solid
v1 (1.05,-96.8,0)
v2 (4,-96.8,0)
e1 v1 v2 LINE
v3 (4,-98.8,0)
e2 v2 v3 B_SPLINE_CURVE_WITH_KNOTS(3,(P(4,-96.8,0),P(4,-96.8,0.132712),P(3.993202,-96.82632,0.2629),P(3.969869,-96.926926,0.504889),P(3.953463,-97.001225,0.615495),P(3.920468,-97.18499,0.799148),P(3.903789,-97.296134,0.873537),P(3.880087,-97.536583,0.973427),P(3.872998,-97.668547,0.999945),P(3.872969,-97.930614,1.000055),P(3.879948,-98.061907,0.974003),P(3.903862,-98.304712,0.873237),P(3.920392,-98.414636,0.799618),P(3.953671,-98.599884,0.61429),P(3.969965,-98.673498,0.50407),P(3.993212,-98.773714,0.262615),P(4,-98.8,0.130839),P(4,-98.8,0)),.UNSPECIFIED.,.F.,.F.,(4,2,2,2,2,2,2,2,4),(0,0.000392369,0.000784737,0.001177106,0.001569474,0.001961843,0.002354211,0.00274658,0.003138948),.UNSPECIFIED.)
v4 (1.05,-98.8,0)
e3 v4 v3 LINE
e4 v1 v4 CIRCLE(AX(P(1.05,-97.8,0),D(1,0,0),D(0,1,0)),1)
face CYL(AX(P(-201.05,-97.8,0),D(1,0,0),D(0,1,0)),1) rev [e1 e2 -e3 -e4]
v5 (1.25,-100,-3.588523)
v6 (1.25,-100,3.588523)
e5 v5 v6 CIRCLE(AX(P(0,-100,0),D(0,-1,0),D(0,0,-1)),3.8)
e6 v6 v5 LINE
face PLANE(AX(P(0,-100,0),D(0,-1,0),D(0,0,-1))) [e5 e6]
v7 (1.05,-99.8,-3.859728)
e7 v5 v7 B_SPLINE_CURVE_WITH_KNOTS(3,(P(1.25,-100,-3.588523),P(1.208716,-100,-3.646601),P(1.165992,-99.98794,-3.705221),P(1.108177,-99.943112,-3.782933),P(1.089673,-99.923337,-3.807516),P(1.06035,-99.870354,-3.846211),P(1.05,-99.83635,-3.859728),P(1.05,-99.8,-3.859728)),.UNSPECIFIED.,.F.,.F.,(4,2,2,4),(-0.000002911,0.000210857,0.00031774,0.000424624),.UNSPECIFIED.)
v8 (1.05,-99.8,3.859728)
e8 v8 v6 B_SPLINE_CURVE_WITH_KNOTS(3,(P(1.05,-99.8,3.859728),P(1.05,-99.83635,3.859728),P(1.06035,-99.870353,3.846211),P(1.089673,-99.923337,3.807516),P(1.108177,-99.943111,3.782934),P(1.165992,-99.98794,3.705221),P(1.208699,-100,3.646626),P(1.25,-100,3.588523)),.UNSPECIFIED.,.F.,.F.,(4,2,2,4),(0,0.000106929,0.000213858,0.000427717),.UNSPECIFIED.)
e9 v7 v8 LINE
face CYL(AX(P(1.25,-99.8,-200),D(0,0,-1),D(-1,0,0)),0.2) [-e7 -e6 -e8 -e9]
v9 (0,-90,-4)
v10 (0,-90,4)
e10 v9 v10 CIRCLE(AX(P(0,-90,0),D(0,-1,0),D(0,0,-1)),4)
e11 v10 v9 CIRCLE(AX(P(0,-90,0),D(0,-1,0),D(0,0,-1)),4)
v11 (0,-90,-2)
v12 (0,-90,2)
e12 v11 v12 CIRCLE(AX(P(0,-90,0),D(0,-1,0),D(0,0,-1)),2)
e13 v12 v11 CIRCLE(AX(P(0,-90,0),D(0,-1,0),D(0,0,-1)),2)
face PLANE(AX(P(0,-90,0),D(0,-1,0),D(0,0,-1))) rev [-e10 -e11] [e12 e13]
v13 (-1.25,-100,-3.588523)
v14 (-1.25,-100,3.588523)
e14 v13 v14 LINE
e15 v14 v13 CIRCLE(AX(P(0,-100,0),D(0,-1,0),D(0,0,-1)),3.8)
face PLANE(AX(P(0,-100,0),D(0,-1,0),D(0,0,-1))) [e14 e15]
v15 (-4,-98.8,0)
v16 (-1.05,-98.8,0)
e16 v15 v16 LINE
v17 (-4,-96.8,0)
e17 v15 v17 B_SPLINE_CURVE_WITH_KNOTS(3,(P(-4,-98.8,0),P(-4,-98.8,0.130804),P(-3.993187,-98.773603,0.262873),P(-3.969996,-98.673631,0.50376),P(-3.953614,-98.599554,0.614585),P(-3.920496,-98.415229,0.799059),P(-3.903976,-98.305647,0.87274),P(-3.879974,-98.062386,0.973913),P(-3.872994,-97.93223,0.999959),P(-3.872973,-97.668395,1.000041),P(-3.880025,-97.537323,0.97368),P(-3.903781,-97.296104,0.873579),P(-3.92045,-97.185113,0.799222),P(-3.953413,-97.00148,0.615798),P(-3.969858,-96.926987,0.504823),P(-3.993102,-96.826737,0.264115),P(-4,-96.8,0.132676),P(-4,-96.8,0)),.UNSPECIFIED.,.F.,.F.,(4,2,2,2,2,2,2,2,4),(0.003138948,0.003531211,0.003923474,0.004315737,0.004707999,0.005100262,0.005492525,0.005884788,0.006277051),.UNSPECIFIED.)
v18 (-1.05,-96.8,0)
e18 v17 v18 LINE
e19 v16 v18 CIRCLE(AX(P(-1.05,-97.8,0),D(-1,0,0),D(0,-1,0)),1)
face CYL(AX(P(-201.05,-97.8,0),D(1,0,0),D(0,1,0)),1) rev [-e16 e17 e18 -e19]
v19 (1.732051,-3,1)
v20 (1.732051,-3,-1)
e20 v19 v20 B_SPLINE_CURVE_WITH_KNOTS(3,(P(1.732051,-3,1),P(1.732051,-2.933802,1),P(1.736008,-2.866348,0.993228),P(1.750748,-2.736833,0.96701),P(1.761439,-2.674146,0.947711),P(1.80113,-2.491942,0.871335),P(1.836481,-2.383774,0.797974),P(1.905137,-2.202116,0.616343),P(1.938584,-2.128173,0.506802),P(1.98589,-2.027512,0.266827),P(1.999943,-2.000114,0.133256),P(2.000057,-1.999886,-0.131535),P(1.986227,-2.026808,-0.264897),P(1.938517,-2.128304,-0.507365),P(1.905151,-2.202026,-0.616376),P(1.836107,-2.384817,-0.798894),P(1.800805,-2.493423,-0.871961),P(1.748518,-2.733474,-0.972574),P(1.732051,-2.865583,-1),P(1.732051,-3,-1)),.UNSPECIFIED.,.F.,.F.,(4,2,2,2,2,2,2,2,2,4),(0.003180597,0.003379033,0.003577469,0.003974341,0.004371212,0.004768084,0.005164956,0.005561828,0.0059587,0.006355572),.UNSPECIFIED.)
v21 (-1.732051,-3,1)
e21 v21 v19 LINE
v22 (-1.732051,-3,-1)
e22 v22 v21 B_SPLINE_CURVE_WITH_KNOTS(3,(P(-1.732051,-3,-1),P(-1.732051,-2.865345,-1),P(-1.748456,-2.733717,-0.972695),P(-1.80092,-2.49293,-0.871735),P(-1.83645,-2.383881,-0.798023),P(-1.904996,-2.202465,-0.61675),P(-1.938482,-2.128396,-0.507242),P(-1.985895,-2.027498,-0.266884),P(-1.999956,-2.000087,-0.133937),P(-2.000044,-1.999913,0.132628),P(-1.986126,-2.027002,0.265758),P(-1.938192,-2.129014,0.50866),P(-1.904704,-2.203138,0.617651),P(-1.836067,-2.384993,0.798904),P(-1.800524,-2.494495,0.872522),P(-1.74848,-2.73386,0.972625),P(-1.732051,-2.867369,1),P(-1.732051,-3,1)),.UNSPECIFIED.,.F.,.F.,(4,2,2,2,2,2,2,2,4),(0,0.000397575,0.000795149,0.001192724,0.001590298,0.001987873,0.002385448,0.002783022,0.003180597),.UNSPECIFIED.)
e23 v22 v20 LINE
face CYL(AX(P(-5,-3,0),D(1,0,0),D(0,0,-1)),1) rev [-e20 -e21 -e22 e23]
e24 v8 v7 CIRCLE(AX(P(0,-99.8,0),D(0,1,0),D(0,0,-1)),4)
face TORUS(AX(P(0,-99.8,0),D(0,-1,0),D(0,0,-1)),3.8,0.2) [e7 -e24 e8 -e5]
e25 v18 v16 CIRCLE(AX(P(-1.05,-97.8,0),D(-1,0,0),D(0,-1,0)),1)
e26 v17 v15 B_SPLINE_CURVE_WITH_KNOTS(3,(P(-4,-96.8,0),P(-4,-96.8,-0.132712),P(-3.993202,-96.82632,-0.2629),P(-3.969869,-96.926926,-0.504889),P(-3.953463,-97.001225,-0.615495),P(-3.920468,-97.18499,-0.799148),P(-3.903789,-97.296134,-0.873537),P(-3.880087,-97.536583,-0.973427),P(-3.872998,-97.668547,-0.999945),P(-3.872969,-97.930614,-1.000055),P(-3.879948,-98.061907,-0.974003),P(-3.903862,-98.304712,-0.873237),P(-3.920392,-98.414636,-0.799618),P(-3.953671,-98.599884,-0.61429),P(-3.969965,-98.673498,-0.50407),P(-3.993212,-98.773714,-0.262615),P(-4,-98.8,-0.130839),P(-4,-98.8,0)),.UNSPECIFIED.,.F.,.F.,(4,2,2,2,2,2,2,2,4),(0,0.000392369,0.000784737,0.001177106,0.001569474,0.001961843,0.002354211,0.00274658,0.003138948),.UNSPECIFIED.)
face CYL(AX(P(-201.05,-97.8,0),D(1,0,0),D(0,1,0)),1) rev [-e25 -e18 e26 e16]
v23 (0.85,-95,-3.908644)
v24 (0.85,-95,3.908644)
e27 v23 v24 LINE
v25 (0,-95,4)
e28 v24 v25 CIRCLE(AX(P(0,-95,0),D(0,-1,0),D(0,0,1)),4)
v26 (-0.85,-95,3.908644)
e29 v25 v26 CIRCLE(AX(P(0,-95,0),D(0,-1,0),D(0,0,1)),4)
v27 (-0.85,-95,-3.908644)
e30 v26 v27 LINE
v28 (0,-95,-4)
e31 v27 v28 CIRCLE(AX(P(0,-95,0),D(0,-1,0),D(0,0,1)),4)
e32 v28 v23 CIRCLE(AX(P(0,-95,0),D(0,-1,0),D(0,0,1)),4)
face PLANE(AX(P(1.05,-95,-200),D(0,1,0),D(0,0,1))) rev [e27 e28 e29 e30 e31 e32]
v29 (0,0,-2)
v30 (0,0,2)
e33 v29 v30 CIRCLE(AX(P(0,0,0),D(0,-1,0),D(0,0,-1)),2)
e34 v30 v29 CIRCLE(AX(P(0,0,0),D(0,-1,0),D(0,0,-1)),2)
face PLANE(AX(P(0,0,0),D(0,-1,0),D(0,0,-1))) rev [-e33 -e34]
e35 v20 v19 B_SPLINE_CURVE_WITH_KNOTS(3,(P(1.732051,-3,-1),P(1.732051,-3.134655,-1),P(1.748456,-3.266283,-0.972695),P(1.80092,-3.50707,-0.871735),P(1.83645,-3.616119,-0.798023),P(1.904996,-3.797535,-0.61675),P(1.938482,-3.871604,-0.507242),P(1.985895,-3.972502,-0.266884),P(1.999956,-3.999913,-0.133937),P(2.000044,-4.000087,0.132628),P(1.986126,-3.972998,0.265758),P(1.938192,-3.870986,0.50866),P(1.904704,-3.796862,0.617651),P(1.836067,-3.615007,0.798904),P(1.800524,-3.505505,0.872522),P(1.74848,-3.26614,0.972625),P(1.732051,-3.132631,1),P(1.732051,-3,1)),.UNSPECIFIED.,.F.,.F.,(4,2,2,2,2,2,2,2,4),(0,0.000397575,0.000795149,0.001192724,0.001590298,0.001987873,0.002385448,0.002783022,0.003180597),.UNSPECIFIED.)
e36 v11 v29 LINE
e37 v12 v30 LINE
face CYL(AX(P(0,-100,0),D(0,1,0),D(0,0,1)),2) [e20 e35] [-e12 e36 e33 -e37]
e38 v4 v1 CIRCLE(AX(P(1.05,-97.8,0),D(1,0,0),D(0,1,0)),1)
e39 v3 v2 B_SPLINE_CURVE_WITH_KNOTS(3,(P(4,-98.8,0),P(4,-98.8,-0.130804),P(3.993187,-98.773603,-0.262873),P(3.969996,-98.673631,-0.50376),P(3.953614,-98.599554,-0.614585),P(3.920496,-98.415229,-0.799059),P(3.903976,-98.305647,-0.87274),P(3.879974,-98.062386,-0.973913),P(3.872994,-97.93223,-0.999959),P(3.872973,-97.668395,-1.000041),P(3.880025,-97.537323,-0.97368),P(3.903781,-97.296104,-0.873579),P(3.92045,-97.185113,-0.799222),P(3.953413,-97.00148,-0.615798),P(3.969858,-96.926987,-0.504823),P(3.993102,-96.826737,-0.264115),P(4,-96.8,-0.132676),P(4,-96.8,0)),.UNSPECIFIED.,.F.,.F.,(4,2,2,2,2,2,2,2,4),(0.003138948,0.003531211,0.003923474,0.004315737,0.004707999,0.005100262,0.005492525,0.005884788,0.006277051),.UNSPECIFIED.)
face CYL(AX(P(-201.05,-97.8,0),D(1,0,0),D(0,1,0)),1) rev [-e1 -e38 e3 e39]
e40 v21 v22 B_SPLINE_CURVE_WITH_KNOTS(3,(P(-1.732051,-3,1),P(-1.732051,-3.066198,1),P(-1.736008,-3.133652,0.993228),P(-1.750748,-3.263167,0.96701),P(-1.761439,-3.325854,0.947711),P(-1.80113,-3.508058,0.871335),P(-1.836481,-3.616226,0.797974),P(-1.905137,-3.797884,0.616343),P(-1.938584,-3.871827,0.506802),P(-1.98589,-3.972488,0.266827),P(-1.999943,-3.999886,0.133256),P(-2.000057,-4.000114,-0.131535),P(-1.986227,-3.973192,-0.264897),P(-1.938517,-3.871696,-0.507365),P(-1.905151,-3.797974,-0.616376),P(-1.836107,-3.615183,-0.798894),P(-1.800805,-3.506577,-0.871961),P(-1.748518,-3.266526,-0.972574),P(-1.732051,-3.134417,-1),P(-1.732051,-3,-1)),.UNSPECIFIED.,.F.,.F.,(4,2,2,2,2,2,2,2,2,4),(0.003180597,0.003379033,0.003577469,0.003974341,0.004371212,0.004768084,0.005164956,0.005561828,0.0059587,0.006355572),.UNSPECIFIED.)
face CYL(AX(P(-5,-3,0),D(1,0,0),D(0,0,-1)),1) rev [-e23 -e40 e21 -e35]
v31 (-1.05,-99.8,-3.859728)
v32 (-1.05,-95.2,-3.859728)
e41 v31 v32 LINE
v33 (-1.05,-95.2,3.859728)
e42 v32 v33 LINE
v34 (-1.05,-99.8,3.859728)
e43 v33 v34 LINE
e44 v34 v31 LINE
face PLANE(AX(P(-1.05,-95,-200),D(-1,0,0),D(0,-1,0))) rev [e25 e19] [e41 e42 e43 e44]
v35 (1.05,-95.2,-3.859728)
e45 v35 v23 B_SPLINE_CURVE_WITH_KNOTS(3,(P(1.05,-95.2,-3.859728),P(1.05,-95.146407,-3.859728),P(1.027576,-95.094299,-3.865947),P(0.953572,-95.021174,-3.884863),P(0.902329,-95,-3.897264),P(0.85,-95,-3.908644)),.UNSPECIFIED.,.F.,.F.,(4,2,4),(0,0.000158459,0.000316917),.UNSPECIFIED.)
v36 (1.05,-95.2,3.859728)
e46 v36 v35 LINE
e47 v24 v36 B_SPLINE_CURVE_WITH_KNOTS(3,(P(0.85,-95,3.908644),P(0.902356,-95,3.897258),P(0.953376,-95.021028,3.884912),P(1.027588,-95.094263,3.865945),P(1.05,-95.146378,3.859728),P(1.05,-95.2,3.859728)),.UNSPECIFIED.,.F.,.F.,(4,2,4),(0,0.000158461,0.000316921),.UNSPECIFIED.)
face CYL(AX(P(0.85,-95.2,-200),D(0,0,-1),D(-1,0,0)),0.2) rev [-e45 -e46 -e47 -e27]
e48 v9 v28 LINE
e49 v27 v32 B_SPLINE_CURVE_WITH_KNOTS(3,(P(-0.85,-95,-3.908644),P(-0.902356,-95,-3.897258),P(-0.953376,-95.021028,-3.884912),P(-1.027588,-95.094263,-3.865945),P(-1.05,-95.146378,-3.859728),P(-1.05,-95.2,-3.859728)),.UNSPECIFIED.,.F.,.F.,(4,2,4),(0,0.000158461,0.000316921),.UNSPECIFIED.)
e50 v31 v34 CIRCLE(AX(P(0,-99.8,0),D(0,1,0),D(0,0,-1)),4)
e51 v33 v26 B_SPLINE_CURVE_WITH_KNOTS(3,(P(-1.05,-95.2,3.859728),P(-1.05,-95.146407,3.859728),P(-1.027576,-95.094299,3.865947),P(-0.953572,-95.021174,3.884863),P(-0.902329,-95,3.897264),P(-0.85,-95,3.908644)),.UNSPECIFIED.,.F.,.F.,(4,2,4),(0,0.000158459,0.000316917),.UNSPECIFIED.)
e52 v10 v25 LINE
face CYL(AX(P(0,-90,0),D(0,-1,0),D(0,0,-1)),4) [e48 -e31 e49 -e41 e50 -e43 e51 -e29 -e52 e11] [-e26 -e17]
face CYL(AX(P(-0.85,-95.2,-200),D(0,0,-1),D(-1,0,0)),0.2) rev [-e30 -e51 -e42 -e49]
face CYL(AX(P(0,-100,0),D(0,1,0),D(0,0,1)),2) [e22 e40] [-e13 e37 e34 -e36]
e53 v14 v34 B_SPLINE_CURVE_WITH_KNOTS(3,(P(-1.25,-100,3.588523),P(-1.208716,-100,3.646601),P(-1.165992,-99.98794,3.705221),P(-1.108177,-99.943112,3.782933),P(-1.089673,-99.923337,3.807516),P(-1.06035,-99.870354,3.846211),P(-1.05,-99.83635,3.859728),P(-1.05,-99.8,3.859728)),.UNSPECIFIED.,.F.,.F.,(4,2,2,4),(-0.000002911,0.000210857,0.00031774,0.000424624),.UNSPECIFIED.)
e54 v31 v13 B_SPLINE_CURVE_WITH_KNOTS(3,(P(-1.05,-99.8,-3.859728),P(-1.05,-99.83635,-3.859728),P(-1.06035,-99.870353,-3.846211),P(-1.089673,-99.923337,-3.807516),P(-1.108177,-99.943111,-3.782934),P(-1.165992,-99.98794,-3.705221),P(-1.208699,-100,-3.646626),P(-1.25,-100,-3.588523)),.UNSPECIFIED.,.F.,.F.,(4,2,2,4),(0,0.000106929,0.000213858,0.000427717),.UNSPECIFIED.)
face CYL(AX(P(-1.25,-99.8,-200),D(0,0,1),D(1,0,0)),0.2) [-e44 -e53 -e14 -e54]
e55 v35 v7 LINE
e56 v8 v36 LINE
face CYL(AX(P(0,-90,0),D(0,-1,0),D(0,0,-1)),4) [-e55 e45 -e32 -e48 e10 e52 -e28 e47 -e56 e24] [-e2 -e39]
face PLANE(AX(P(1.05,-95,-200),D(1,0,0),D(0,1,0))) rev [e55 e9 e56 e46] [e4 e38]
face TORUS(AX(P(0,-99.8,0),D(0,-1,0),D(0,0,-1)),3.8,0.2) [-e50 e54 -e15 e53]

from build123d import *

# Parameters (mm, degrees)
SKETCH_11_R         = 2
EXTRUDE_3_DEPTH     = 100
SKETCH_20_R         = 4
EXTRUDE_4_DEPTH     = 10
SKETCH_16_W         = 2.1
SKETCH_16_H         = 5
CUT_EXTRUDE_5_DEPTH = 200
SKETCH_18_R         = 1
CUT_EXTRUDE_7_DEPTH = 200
SKETCH_19_R         = 1
CUT_EXTRUDE_8_DEPTH = 5
FILLET_1_R          = 0.2
FILLET_2_R          = 0.2


with BuildPart() as part:
    # 草图11 → 凸台-拉伸3 (new body)
    with BuildSketch(Plane.XZ):
        with Locations(Location((0, 0, 0), (0, 0, 270))):
            Circle(SKETCH_11_R)
    extrude(amount=EXTRUDE_3_DEPTH)

    # 草图20 → 凸台-拉伸4 (add)
    with BuildSketch(Plane.XZ.offset(100)):
        with Locations(Location((0, 0, 0), (0, 0, 270))):
            Circle(SKETCH_20_R)
    extrude(amount=-EXTRUDE_4_DEPTH)

    # 草图16 → 切除-拉伸5 (cut, symmetric)
    with BuildSketch(Plane.XY):
        with Locations((0, -97.5)):
            Rectangle(SKETCH_16_W, SKETCH_16_H)
    extrude(amount=CUT_EXTRUDE_5_DEPTH, both=True, mode=Mode.SUBTRACT)

    # 草图18 → 切除-拉伸7 (cut, symmetric)
    with BuildSketch(Plane(origin=(-1.05, 0, 0), x_dir=(0, 0, -1), z_dir=(1, 0, 0))):
        with Locations(Location((0, -97.8, 0), (0, 0, 90))):
            Circle(SKETCH_18_R)
    extrude(amount=CUT_EXTRUDE_7_DEPTH, both=True, mode=Mode.SUBTRACT)

    # 草图19 → 切除-拉伸8 (cut, symmetric)
    with BuildSketch(Plane(origin=(0, 0, 0), x_dir=(0, 0, -1), z_dir=(1, 0, 0))):
        with Locations((0, -3)):
            Circle(SKETCH_19_R)
    extrude(amount=CUT_EXTRUDE_8_DEPTH, both=True, mode=Mode.SUBTRACT)

    # 圆角1
    fillet_1_edges = [part.edges().sort_by_distance(p)[0] for p in [
        (-4, -100, 0),
        (1.05, -100, 0),
        (-1.05, -100, 0),
        (4, -100, 0),
    ]]
    fillet(fillet_1_edges, radius=FILLET_1_R)

    # 圆角2
    fillet_2_edges = [part.edges().sort_by_distance(p)[0] for p in [
        (-1.05, -95, 0),
        (1.05, -95, 0),
    ]]
    fillet(fillet_2_edges, radius=FILLET_2_R)


solid = part.part
